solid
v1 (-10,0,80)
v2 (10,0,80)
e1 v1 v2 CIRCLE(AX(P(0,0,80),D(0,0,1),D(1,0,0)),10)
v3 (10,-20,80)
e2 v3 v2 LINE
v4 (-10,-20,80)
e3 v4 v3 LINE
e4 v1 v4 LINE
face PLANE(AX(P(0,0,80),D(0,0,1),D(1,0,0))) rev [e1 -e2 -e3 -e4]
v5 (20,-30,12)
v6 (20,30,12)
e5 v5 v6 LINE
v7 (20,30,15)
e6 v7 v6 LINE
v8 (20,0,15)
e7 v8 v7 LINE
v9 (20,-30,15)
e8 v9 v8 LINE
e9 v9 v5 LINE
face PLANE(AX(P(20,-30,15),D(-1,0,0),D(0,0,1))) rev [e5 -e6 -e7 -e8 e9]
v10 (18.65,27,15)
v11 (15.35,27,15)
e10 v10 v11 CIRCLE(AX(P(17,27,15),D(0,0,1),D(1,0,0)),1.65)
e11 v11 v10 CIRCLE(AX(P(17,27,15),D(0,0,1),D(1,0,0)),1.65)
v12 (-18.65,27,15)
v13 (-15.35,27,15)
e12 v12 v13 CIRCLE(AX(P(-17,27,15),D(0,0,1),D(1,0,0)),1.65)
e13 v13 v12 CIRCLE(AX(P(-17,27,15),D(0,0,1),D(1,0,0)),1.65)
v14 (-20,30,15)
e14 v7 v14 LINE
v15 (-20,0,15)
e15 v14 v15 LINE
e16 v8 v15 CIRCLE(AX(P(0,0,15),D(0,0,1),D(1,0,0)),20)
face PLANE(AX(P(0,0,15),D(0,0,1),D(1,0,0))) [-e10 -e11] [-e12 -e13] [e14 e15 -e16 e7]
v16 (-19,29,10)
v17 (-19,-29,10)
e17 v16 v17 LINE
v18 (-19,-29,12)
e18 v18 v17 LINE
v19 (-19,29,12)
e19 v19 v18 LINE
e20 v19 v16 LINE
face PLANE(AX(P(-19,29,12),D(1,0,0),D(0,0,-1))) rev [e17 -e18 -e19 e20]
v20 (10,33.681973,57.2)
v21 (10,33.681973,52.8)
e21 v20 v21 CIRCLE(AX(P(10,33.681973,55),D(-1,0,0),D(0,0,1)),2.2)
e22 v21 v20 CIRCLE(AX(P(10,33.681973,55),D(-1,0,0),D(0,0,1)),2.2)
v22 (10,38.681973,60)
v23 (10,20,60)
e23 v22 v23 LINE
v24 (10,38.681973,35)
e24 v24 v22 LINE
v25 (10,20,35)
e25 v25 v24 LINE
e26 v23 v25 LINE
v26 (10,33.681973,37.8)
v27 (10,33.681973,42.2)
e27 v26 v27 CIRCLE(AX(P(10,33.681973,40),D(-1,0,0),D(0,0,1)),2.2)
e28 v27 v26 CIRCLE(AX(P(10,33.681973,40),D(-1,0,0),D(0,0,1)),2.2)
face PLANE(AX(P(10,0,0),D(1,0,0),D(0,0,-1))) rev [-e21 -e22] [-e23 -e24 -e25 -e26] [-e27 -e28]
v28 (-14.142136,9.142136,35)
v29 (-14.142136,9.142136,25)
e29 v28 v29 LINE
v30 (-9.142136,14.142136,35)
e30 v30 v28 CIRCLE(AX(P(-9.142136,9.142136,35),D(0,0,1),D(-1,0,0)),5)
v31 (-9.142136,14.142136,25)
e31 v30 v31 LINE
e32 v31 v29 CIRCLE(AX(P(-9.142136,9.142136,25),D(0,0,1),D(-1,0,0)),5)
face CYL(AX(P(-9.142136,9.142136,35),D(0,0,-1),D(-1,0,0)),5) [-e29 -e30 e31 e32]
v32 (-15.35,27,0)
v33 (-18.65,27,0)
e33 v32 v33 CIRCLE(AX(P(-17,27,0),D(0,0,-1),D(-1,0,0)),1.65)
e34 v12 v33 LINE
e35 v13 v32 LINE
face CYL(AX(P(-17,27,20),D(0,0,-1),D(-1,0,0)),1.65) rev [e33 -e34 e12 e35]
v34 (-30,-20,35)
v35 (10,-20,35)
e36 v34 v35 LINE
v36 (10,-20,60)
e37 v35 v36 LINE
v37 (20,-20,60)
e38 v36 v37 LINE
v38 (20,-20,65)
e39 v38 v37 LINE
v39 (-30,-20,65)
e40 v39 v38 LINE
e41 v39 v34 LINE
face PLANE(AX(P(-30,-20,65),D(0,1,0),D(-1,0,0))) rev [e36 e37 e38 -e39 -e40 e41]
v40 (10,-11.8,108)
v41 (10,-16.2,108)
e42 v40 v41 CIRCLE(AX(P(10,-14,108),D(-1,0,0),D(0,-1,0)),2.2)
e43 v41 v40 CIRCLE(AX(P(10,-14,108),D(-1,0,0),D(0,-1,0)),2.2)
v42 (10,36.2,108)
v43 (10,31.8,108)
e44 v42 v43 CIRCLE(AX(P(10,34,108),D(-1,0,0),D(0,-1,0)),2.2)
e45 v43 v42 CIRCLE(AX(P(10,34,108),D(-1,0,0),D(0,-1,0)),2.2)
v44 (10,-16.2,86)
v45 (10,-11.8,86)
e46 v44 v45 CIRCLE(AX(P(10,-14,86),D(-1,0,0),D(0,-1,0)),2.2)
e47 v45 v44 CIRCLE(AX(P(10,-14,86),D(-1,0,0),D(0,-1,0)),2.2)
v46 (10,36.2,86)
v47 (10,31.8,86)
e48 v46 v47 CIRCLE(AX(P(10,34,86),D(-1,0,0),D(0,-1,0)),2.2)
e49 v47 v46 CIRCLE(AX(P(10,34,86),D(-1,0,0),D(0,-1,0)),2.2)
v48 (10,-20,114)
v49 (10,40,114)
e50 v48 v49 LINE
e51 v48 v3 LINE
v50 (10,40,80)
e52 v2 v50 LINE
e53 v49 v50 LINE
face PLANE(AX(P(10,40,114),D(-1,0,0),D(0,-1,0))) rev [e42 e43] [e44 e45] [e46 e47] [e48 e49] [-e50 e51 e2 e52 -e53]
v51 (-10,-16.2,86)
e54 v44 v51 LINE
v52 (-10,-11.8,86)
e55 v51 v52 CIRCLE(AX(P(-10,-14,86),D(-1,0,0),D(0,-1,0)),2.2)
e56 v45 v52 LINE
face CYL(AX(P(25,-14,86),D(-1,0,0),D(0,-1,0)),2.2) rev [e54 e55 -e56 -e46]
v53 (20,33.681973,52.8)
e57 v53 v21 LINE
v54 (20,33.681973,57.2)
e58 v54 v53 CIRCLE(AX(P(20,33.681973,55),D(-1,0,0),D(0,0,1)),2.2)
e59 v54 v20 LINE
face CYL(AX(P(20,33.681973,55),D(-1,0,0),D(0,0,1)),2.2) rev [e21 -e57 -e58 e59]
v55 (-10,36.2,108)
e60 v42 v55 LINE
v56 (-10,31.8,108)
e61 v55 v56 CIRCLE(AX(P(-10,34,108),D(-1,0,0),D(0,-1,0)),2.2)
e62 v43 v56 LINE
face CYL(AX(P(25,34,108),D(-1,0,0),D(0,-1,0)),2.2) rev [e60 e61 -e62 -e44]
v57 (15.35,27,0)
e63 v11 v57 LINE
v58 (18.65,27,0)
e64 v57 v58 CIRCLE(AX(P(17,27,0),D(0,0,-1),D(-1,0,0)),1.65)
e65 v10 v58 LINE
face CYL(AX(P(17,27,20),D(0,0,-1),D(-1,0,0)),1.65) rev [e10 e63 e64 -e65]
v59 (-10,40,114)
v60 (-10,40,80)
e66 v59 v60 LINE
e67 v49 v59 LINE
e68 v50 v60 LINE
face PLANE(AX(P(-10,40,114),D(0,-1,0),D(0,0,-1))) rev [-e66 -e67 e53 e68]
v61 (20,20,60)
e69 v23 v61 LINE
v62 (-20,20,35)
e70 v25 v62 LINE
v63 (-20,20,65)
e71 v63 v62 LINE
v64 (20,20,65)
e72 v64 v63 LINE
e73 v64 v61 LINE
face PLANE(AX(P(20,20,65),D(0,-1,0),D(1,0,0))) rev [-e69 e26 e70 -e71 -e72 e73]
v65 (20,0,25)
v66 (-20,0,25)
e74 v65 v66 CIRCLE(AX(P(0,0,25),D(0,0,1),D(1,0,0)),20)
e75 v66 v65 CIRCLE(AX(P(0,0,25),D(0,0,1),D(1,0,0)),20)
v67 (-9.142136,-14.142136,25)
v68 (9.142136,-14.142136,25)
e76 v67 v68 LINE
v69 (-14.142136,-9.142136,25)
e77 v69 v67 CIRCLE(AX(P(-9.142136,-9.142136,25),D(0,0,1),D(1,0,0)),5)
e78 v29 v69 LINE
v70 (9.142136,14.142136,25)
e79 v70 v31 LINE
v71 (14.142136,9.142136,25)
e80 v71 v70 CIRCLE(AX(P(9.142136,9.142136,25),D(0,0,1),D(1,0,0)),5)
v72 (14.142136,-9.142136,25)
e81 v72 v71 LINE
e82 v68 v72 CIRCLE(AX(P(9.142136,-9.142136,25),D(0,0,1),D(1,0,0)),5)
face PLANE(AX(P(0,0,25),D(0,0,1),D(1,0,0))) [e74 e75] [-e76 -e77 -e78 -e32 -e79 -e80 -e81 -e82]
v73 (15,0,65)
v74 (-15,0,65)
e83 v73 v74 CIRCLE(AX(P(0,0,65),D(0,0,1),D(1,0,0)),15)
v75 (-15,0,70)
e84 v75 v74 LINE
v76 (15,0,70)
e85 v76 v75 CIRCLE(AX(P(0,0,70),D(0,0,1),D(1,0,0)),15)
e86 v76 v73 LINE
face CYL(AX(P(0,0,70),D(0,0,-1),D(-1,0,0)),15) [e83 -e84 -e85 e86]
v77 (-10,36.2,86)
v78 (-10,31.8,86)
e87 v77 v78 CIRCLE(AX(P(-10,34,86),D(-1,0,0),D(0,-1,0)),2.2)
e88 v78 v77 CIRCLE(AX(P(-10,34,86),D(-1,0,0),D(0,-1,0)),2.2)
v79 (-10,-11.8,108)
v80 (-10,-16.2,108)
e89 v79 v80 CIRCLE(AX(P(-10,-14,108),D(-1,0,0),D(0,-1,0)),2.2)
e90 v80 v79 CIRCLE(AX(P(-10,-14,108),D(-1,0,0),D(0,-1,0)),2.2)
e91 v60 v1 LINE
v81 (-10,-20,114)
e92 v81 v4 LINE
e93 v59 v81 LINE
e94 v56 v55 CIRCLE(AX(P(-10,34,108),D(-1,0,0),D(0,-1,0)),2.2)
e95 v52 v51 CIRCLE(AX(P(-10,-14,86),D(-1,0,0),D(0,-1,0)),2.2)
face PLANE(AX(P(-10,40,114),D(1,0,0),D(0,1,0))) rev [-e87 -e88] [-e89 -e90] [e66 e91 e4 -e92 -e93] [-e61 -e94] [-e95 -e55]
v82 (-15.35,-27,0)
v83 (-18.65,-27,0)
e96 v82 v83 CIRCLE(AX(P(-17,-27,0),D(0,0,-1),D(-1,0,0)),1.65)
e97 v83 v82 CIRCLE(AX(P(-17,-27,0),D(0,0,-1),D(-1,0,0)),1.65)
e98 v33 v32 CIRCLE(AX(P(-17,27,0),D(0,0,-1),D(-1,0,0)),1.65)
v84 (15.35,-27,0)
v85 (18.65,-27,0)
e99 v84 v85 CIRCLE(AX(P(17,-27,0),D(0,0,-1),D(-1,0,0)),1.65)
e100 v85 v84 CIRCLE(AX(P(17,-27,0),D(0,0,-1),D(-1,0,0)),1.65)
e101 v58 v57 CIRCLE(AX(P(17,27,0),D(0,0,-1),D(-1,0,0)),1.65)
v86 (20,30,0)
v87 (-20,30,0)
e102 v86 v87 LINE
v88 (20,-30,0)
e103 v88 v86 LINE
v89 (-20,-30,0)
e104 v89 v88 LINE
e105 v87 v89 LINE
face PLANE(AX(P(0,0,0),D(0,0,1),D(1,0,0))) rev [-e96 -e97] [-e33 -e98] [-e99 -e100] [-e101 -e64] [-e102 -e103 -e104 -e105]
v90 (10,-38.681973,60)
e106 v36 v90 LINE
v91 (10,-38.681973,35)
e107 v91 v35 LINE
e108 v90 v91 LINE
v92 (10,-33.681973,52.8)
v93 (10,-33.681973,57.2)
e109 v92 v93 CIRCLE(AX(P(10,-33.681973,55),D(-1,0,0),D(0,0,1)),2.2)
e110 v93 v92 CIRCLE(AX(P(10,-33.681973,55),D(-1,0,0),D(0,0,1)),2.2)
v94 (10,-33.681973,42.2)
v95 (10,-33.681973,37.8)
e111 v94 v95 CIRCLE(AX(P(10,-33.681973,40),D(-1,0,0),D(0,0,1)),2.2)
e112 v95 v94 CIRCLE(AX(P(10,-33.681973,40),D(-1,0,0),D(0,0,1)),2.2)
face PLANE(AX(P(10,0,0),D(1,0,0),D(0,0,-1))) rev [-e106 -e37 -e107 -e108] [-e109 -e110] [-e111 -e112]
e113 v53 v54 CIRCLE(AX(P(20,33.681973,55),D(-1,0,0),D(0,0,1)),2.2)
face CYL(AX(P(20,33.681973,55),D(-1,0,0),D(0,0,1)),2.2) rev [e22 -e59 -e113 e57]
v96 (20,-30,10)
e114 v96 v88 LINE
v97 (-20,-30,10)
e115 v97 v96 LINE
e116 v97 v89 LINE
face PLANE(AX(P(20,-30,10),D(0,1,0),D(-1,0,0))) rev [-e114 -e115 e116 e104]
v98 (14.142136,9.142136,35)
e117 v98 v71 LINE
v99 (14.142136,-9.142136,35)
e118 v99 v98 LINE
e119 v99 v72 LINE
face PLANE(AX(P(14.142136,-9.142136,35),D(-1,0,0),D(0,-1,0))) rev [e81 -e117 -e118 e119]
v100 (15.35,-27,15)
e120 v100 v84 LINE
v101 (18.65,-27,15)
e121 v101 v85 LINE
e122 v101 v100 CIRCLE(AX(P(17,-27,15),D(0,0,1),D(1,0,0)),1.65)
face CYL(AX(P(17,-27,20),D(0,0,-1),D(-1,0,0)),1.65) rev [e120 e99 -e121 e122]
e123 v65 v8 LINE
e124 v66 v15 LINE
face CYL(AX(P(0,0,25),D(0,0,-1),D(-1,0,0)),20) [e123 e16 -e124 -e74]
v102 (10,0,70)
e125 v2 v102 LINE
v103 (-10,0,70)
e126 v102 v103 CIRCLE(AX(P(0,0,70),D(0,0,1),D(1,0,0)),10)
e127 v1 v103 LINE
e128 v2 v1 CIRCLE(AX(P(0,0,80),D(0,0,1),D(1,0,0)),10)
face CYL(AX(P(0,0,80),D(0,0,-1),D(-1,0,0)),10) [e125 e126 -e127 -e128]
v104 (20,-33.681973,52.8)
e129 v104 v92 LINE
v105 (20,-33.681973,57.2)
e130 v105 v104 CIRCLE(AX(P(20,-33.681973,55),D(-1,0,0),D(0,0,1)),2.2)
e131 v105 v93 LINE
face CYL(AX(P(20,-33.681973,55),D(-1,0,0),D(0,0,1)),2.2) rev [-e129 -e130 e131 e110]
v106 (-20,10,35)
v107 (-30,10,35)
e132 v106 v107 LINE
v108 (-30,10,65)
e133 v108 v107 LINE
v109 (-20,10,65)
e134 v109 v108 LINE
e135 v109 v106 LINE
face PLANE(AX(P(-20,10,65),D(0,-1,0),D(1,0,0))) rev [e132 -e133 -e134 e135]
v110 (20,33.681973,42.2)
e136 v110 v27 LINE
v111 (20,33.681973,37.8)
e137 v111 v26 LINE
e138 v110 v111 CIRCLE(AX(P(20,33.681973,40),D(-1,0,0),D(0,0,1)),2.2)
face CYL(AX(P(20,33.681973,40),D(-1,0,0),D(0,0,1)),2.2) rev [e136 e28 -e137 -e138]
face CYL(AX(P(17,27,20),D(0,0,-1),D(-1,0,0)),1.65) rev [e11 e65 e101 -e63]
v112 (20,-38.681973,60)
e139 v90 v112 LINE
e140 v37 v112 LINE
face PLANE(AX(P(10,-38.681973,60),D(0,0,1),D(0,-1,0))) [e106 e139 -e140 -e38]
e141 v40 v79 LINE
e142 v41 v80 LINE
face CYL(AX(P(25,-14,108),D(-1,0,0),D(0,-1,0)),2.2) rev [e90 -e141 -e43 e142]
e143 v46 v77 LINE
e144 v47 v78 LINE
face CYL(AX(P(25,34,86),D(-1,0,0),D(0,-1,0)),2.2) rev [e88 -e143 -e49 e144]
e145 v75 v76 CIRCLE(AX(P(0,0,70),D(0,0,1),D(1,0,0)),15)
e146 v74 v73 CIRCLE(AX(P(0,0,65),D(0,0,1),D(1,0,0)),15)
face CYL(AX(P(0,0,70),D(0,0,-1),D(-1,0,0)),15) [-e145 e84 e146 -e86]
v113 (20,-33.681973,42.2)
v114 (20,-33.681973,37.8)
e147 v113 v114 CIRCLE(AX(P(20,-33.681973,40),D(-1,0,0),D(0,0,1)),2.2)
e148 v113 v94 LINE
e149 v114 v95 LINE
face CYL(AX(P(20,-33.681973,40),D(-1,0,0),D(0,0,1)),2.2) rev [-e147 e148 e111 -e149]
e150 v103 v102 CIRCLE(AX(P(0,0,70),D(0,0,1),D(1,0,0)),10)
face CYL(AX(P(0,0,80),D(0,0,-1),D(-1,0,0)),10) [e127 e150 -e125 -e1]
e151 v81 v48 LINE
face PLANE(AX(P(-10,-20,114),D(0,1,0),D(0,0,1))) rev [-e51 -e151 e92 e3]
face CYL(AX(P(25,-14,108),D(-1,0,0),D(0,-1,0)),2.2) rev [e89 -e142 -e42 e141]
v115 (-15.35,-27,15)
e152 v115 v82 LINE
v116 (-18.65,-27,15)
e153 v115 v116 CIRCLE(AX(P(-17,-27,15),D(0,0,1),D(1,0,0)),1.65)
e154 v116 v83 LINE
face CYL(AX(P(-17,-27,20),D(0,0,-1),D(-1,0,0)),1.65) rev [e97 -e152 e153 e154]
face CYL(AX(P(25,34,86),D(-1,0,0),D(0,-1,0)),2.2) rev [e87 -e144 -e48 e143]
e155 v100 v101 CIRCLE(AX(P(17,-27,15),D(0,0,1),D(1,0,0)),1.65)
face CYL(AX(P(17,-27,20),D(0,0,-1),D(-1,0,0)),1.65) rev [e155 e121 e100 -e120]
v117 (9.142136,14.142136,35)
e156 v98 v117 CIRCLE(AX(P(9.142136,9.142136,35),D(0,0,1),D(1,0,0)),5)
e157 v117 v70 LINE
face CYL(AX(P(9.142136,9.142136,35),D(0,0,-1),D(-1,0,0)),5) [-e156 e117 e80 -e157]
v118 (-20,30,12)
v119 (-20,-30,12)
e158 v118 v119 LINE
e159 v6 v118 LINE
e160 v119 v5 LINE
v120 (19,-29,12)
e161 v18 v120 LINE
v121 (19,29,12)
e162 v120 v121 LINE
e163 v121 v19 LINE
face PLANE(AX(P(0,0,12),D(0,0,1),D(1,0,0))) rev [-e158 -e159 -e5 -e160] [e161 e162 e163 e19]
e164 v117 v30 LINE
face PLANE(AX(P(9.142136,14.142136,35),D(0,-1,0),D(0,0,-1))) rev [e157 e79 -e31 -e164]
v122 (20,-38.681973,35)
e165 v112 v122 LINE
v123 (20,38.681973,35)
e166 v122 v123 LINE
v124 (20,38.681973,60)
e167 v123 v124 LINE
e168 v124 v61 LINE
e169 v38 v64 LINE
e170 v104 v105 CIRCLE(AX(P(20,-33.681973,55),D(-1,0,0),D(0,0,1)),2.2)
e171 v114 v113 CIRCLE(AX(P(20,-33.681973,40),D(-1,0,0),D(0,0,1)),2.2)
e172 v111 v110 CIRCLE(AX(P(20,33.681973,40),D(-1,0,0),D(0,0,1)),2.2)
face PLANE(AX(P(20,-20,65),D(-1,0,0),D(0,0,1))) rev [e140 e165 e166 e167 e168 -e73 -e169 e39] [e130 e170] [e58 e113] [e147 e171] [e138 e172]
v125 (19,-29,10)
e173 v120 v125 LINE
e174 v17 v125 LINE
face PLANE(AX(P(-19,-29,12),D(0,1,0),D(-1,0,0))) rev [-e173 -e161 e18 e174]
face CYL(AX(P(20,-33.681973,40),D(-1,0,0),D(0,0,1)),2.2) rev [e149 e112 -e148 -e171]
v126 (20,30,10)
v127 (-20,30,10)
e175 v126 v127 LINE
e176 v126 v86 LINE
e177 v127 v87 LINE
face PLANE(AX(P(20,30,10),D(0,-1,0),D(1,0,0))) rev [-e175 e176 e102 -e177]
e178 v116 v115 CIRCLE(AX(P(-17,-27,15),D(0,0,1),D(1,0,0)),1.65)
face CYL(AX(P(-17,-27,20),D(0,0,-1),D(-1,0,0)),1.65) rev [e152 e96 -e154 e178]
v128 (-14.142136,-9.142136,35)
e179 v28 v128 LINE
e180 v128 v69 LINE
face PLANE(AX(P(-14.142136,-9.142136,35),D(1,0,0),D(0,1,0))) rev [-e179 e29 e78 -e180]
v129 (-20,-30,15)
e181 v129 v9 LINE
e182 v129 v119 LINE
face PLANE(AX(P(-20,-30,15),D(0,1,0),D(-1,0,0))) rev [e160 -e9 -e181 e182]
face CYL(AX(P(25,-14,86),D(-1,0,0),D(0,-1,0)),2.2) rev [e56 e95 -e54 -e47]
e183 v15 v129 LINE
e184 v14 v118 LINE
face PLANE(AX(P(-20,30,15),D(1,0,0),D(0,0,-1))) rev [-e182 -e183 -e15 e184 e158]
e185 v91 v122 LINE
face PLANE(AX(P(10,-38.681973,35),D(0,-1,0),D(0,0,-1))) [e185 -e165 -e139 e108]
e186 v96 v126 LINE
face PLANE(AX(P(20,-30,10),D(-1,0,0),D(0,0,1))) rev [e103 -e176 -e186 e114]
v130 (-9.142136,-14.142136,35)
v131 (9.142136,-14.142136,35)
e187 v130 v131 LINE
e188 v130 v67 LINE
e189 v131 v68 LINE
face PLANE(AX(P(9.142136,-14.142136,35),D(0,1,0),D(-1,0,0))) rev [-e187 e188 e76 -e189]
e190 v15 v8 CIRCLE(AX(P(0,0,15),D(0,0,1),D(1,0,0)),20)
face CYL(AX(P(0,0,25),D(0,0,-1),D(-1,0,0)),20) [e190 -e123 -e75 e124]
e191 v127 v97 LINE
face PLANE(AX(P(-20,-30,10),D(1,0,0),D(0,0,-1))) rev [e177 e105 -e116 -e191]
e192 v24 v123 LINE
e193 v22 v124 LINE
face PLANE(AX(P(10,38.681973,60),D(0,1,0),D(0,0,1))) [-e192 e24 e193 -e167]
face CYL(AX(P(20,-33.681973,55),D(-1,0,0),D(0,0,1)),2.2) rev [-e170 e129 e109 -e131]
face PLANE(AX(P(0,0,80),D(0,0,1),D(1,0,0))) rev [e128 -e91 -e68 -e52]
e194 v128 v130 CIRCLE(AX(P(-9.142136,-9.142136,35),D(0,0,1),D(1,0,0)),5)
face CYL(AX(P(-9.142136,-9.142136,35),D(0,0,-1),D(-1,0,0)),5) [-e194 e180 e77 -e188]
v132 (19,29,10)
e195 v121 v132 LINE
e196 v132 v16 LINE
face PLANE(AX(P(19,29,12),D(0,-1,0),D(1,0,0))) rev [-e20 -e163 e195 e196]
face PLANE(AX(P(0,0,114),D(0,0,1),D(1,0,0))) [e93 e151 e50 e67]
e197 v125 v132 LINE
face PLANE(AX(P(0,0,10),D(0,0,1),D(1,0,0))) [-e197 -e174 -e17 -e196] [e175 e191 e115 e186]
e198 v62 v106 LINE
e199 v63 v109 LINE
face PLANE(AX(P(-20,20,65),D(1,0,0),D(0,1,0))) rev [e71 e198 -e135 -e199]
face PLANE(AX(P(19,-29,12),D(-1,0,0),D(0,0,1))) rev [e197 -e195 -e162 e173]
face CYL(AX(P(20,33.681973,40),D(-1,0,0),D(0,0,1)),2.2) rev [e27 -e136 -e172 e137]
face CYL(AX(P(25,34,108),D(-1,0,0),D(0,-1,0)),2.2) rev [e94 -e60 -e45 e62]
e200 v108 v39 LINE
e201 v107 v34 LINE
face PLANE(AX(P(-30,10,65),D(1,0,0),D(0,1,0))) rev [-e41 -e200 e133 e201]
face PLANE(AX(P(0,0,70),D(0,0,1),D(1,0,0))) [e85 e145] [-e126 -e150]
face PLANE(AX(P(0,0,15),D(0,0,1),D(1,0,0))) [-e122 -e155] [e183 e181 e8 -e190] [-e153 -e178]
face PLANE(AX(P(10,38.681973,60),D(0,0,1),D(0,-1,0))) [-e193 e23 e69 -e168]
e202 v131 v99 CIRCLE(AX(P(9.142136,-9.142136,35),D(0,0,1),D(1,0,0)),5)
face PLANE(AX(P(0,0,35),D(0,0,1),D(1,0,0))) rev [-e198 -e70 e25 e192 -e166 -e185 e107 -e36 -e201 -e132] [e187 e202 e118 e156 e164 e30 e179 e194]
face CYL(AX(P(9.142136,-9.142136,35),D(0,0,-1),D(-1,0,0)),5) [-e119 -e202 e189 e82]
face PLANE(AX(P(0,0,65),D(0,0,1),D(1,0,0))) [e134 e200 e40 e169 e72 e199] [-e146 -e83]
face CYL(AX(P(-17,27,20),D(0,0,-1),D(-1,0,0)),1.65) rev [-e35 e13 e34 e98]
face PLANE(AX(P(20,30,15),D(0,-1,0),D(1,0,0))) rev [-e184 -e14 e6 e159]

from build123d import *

# Parameters (mm, degrees)
SKETCH_1_W          = 40
SKETCH_1_H          = 60
EXTRUDE_1_DEPTH     = 10
SKETCH_2_W          = 38
SKETCH_2_H          = 58
EXTRUDE_2_DEPTH     = 2
SKETCH_3_W          = 40
SKETCH_3_H          = 60
EXTRUDE_3_DEPTH     = 3
SKETCH_4_R          = 20
EXTRUDE_4_DEPTH     = 10
EXTRUDE_5_DEPTH     = 10
SKETCH_6_R          = 1.65
CUT_EXTRUDE_1_DEPTH = 20
EXTRUDE_6_DEPTH     = 30
SKETCH_8_R          = 15
EXTRUDE_7_DEPTH     = 5
SKETCH_9_R          = 10
EXTRUDE_8_DEPTH     = 10
SKETCH_10_W         = 25
SKETCH_10_H         = 18.68197258
EXTRUDE_9_DEPTH     = 10
SKETCH_11_R         = 2.2
CUT_EXTRUDE_2_DEPTH = 10
SKETCH_12_W         = 20
SKETCH_12_H         = 60
EXTRUDE_10_DEPTH    = 34
SKETCH_13_R         = 2.2
CUT_EXTRUDE_3_DEPTH = 35


with BuildPart() as part:
    # 草图1 → 凸台-拉伸1 (new body)
    with BuildSketch(Plane.XY):
        Rectangle(SKETCH_1_W, SKETCH_1_H)
    extrude(amount=EXTRUDE_1_DEPTH)

    # 草图2 → 凸台-拉伸2 (add)
    with BuildSketch(Plane.XY.offset(10)):
        Rectangle(SKETCH_2_W, SKETCH_2_H)
    extrude(amount=EXTRUDE_2_DEPTH)

    # 草图3 → 凸台-拉伸3 (add)
    with BuildSketch(Plane.XY.offset(12)):
        Rectangle(SKETCH_3_W, SKETCH_3_H)
    extrude(amount=EXTRUDE_3_DEPTH)

    # 草图4 → 凸台-拉伸4 (add)
    with BuildSketch(Plane.XY.offset(15)):
        Circle(SKETCH_4_R)
    extrude(amount=EXTRUDE_4_DEPTH)

    # 草图5 → 凸台-拉伸5 (add)
    with BuildSketch(Plane.XY.offset(25)):
        with BuildLine():
            Line((9.142135624, -14.142135624), (-9.142135624, -14.142135624))
            ThreePointArc((-9.142135624, -14.142135624), (-12.67766953, -12.67766953), (-14.142135624, -9.142135624))
            Line((-14.142135624, -9.142135624), (-14.142135624, 9.142135624))
            ThreePointArc((-14.142135624, 9.142135624), (-12.67766953, 12.67766953), (-9.142135624, 14.142135624))
            Line((-9.142135624, 14.142135624), (9.142135624, 14.142135624))
            ThreePointArc((9.142135624, 14.142135624), (12.67766953, 12.67766953), (14.142135624, 9.142135624))
            Line((14.142135624, 9.142135624), (14.142135624, -9.142135624))
            ThreePointArc((14.142135624, -9.142135624), (12.67766953, -12.67766953), (9.142135624, -14.142135624))
        make_face()
    extrude(amount=EXTRUDE_5_DEPTH)

    # 草图6 → 切除-拉伸1 (cut)
    with BuildSketch(Plane(origin=(0, 0, 0), x_dir=(-1, 0, 0), z_dir=(0, 0, -1))):
        with Locations((17, 27)):
            Circle(SKETCH_6_R)
        with Locations((17, -27)):
            Circle(SKETCH_6_R)
        with Locations((-17, -27)):
            Circle(SKETCH_6_R)
        with Locations((-17, 27)):
            Circle(SKETCH_6_R)
    extrude(amount=-CUT_EXTRUDE_1_DEPTH, mode=Mode.SUBTRACT)

    # 草图7 → 凸台-拉伸6 (add)
    with BuildSketch(Plane.XY.offset(35)):
        Polygon((20, -20), (20, 20), (-20, 20), (-20, 10), (-30, 10), (-30, -20), align=None)
    extrude(amount=EXTRUDE_6_DEPTH)

    # 草图8 → 凸台-拉伸7 (add)
    with BuildSketch(Plane.XY.offset(65)):
        Circle(SKETCH_8_R)
    extrude(amount=EXTRUDE_7_DEPTH)

    # 草图9 → 凸台-拉伸8 (add)
    with BuildSketch(Plane.XY.offset(70)):
        Circle(SKETCH_9_R)
    extrude(amount=EXTRUDE_8_DEPTH)

    # 草图10 → 凸台-拉伸9 (add)
    with BuildSketch(Plane(origin=(20, 0, 0), x_dir=(0, 0, -1), z_dir=(1, 0, 0))):
        with Locations((-47.5, 29.34098629)):
            Rectangle(SKETCH_10_W, SKETCH_10_H)
        with Locations((-47.5, -29.34098629)):
            Rectangle(SKETCH_10_W, SKETCH_10_H)
    extrude(amount=-EXTRUDE_9_DEPTH)

    # 草图11 → 切除-拉伸2 (cut)
    with BuildSketch(Plane.ZY.offset(-10)):
        with Locations((55, 33.68197258)):
            Circle(SKETCH_11_R)
        with Locations((40, 33.68197258)):
            Circle(SKETCH_11_R)
        with Locations((40, -33.68197258)):
            Circle(SKETCH_11_R)
        with Locations((55, -33.68197258)):
            Circle(SKETCH_11_R)
    extrude(amount=-CUT_EXTRUDE_2_DEPTH, mode=Mode.SUBTRACT)

    # 草图12 → 凸台-拉伸10 (add)
    with BuildSketch(Plane.XY.offset(80)):
        with Locations((0, 10)):
            Rectangle(SKETCH_12_W, SKETCH_12_H)
    extrude(amount=EXTRUDE_10_DEPTH)

    # 草图13 → 切除-拉伸3 (cut)
    with BuildSketch(Plane.ZY.offset(10)):
        with Locations(Location((108, 34, 0), (0, 0, 270))):
            Circle(SKETCH_13_R)
        with Locations(Location((86, 34, 0), (0, 0, 270))):
            Circle(SKETCH_13_R)
        with Locations(Location((108, -14, 0), (0, 0, 270))):
            Circle(SKETCH_13_R)
        with Locations(Location((86, -14, 0), (0, 0, 270))):
            Circle(SKETCH_13_R)
    extrude(amount=-CUT_EXTRUDE_3_DEPTH, mode=Mode.SUBTRACT)


solid = part.part
